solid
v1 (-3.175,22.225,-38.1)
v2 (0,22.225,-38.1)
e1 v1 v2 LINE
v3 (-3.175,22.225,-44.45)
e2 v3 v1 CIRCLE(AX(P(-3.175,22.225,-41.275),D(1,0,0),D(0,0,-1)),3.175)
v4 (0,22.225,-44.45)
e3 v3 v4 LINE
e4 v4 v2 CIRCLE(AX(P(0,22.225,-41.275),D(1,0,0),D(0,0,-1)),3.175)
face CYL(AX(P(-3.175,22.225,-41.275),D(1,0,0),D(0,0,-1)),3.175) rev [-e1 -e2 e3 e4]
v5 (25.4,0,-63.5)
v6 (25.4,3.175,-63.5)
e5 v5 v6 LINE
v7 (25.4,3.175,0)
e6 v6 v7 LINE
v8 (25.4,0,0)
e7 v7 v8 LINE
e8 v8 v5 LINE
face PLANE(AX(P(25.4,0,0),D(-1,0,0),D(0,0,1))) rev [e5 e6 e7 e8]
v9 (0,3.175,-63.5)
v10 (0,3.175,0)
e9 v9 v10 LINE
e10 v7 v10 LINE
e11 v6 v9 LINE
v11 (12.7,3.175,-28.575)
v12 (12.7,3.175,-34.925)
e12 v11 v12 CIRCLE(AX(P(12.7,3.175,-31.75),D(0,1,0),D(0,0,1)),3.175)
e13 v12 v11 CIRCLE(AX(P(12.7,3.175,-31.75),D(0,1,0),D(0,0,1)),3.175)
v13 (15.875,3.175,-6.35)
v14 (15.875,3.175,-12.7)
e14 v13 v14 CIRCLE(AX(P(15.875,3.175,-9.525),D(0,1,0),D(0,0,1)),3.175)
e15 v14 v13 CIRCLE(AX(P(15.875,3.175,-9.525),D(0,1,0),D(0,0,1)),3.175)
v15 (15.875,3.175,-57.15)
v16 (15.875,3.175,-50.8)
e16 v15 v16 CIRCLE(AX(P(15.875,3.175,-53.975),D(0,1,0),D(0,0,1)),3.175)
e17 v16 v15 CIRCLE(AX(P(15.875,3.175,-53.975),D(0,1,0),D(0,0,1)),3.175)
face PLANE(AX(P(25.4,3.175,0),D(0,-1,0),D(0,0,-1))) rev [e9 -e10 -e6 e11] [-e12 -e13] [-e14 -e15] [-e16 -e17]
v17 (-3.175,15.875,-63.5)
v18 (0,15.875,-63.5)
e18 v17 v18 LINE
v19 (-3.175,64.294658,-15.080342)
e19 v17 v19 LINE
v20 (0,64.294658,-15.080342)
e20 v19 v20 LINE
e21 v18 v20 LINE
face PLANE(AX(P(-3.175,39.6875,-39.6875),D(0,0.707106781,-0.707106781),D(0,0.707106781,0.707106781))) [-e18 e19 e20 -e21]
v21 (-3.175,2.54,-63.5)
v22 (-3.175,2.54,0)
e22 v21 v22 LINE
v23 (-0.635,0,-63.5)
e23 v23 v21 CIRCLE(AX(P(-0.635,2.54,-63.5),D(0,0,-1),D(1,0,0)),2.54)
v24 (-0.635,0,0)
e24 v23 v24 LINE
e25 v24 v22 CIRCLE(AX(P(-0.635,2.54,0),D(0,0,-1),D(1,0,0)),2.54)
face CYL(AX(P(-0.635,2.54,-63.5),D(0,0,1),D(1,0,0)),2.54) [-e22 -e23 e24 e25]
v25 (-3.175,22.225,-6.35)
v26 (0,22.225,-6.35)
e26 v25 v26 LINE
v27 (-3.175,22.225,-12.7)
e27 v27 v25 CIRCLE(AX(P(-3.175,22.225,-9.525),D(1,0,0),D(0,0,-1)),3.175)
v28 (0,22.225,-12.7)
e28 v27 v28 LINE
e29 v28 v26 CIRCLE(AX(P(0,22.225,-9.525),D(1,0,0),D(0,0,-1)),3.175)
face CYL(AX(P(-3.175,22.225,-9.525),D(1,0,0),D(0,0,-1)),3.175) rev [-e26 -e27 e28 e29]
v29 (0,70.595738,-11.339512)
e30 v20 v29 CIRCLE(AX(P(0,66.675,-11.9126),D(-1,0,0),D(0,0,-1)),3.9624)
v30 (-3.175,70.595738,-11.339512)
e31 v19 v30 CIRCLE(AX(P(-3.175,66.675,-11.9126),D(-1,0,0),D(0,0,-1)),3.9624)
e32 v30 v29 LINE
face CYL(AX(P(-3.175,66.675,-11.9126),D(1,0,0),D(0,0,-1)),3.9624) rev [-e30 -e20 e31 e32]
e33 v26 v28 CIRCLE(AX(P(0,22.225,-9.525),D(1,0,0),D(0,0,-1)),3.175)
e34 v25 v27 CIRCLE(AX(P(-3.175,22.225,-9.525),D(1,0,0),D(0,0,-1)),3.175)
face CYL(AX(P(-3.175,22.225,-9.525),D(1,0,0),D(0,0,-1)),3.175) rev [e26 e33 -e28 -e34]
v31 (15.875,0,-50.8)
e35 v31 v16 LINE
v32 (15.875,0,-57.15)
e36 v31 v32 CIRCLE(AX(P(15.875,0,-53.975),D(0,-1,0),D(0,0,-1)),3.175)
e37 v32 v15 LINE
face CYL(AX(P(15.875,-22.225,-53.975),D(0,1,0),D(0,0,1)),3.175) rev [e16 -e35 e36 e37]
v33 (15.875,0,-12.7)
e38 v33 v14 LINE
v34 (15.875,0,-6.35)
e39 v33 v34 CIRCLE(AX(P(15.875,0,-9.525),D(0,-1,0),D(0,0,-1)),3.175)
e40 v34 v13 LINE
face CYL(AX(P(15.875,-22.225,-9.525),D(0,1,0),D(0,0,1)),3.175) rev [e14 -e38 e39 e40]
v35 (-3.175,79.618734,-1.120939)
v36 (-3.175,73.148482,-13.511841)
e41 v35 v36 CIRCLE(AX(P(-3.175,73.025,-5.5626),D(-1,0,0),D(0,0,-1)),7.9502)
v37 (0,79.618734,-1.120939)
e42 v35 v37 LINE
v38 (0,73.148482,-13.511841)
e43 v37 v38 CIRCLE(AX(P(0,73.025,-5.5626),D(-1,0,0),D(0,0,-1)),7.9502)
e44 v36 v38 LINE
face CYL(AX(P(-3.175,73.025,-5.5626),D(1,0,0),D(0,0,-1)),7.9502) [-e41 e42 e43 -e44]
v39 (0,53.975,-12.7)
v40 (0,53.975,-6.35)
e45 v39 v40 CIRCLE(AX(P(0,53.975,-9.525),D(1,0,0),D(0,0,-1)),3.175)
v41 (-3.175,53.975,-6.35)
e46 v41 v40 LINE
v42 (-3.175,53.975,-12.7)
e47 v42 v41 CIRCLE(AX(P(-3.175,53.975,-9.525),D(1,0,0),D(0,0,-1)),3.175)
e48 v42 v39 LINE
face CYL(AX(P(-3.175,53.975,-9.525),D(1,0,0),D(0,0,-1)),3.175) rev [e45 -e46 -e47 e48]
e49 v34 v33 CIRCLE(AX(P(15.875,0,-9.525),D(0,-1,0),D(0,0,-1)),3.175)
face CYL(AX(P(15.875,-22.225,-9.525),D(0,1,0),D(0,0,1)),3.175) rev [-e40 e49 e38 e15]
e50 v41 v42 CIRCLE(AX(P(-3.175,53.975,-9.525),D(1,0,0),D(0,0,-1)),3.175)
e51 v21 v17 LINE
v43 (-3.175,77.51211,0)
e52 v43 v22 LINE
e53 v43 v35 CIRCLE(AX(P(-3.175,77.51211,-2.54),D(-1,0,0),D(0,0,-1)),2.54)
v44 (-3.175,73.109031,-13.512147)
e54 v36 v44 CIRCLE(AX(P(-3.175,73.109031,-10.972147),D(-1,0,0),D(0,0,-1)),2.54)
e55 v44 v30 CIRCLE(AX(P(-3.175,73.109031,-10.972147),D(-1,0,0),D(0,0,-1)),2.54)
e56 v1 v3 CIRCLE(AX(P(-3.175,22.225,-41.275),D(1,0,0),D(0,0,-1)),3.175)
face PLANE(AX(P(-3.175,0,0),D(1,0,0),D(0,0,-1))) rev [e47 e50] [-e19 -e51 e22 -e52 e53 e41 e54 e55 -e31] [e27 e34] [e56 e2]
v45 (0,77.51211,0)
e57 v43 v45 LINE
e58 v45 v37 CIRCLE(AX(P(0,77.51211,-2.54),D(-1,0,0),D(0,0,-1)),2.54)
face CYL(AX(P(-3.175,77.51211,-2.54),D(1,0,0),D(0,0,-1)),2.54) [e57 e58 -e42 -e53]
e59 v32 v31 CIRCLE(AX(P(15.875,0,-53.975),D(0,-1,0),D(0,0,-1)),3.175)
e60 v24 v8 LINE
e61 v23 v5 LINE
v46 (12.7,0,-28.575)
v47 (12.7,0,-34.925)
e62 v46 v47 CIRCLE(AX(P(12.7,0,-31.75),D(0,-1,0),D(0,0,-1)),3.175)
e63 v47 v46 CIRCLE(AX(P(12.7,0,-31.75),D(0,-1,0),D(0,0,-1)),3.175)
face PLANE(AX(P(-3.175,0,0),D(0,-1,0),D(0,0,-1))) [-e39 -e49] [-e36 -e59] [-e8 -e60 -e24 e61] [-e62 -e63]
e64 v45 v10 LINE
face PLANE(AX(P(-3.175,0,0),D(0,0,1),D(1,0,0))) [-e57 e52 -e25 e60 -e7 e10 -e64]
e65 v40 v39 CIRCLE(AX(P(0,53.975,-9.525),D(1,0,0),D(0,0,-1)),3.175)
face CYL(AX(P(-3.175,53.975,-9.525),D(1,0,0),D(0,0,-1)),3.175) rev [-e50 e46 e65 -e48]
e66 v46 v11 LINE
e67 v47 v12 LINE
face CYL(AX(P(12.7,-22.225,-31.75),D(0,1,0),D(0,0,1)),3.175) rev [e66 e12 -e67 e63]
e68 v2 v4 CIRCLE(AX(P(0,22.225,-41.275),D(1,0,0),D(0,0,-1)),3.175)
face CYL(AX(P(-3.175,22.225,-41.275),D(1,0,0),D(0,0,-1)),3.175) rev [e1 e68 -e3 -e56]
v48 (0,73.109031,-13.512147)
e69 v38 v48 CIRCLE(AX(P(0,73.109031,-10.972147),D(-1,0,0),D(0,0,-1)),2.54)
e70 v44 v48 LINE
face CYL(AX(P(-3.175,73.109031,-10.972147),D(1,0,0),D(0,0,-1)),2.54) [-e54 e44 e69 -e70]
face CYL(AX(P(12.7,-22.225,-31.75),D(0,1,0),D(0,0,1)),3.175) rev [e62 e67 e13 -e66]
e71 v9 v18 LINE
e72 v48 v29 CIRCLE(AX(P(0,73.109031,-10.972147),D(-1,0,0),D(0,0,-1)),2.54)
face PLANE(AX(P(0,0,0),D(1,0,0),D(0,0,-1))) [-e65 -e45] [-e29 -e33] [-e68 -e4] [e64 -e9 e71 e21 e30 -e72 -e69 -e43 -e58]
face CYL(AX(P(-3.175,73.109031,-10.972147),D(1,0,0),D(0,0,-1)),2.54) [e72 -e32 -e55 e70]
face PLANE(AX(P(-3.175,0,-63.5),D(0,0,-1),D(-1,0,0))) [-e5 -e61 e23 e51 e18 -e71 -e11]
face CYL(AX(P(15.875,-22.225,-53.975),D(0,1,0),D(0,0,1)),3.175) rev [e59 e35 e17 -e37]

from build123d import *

# Parameters (mm, degrees)
SKETCH1_R           = 3.175
SKETCH1_W           = 63.5
SKETCH1_H           = 3.175
BOSS_EXTRUDE1_DEPTH = 3.175
SKETCH2_W           = 63.5
SKETCH2_H           = 3.175
BOSS_EXTRUDE2_DEPTH = 25.4
CUT_EXTRUDE1_DEPTH  = 106.992419611
SKETCH4_R           = 3.175
CUT_EXTRUDE2_DEPTH  = 25.4


with BuildPart() as part:
    # Sketch1 → Boss-Extrude1 (new body)
    # profile 1 of 2: a face of its own
    with BuildSketch(Plane(origin=(0, 0, 0), x_dir=(0, 0, -1), z_dir=(1, 0, 0))):
        with BuildLine():
            Line((0, 77.51210968), (0, 3.175))
            Line((0, 3.175), (63.5, 3.175))
            Line((63.5, 3.175), (63.5, 15.875))
            Line((63.5, 15.875), (15.080341671, 64.294658329))
            ThreePointArc((15.080341671, 64.294658329), (8.505408108, 64.65221549), (11.339511683, 70.595737627))
            ThreePointArc((11.339511683, 70.595737627), (12.906539417, 71.462906002), (13.511840983, 73.148482141))
            ThreePointArc((13.511840983, 73.148482141), (9.242521041, 80.072259125), (1.120938967, 79.618733943))
            ThreePointArc((1.120938967, 79.618733943), (0.297678098, 78.705253631), (0, 77.51210968))
        make_face()
        with Locations((9.525, 22.225)):
            Circle(SKETCH1_R, mode=Mode.SUBTRACT)
        with Locations((41.275, 22.225)):
            Circle(SKETCH1_R, mode=Mode.SUBTRACT)
        with Locations((9.525, 53.975)):
            Circle(SKETCH1_R, mode=Mode.SUBTRACT)
    # profile 2 of 2: a face of its own
    with BuildSketch(Plane(origin=(0, 0, 0), x_dir=(0, 0, -1), z_dir=(1, 0, 0))):
        with Locations((31.75, 1.5875)):
            Rectangle(SKETCH1_W, SKETCH1_H)
    extrude(amount=-BOSS_EXTRUDE1_DEPTH)

    # Sketch2 → Boss-Extrude2 (add)
    with BuildSketch(Plane(origin=(0, 0, 0), x_dir=(0, 0, -1), z_dir=(1, 0, 0))):
        with Locations((31.75, 1.5875)):
            Rectangle(SKETCH2_W, SKETCH2_H)
    extrude(amount=BOSS_EXTRUDE2_DEPTH)

    # Sketch3 → Cut-Extrude1 (cut, through all)
    with BuildSketch(Plane.XY):
        with BuildLine():
            ThreePointArc((-0.635, 0), (-2.431051224, 0.743948776), (-3.175, 2.54))
            Line((-3.175, 2.54), (-3.175, 0))
            Line((-3.175, 0), (-0.635, 0))
        make_face()
    extrude(amount=-CUT_EXTRUDE1_DEPTH, mode=Mode.SUBTRACT)

    # Sketch4 → Cut-Extrude2 (cut)
    with BuildSketch(Plane(origin=(0, 3.175, 0), x_dir=(1, 0, 0), z_dir=(0, 1, 0))):
        with Locations(Location((15.875, 53.975, 0), (0, 0, 270))):
            Circle(SKETCH4_R)
        with Locations(Location((12.7, 31.75, 0), (0, 0, 270))):
            Circle(SKETCH4_R)
        with Locations(Location((15.875, 9.525, 0), (0, 0, 270))):
            Circle(SKETCH4_R)
    extrude(amount=-CUT_EXTRUDE2_DEPTH, mode=Mode.SUBTRACT)


solid = part.part
